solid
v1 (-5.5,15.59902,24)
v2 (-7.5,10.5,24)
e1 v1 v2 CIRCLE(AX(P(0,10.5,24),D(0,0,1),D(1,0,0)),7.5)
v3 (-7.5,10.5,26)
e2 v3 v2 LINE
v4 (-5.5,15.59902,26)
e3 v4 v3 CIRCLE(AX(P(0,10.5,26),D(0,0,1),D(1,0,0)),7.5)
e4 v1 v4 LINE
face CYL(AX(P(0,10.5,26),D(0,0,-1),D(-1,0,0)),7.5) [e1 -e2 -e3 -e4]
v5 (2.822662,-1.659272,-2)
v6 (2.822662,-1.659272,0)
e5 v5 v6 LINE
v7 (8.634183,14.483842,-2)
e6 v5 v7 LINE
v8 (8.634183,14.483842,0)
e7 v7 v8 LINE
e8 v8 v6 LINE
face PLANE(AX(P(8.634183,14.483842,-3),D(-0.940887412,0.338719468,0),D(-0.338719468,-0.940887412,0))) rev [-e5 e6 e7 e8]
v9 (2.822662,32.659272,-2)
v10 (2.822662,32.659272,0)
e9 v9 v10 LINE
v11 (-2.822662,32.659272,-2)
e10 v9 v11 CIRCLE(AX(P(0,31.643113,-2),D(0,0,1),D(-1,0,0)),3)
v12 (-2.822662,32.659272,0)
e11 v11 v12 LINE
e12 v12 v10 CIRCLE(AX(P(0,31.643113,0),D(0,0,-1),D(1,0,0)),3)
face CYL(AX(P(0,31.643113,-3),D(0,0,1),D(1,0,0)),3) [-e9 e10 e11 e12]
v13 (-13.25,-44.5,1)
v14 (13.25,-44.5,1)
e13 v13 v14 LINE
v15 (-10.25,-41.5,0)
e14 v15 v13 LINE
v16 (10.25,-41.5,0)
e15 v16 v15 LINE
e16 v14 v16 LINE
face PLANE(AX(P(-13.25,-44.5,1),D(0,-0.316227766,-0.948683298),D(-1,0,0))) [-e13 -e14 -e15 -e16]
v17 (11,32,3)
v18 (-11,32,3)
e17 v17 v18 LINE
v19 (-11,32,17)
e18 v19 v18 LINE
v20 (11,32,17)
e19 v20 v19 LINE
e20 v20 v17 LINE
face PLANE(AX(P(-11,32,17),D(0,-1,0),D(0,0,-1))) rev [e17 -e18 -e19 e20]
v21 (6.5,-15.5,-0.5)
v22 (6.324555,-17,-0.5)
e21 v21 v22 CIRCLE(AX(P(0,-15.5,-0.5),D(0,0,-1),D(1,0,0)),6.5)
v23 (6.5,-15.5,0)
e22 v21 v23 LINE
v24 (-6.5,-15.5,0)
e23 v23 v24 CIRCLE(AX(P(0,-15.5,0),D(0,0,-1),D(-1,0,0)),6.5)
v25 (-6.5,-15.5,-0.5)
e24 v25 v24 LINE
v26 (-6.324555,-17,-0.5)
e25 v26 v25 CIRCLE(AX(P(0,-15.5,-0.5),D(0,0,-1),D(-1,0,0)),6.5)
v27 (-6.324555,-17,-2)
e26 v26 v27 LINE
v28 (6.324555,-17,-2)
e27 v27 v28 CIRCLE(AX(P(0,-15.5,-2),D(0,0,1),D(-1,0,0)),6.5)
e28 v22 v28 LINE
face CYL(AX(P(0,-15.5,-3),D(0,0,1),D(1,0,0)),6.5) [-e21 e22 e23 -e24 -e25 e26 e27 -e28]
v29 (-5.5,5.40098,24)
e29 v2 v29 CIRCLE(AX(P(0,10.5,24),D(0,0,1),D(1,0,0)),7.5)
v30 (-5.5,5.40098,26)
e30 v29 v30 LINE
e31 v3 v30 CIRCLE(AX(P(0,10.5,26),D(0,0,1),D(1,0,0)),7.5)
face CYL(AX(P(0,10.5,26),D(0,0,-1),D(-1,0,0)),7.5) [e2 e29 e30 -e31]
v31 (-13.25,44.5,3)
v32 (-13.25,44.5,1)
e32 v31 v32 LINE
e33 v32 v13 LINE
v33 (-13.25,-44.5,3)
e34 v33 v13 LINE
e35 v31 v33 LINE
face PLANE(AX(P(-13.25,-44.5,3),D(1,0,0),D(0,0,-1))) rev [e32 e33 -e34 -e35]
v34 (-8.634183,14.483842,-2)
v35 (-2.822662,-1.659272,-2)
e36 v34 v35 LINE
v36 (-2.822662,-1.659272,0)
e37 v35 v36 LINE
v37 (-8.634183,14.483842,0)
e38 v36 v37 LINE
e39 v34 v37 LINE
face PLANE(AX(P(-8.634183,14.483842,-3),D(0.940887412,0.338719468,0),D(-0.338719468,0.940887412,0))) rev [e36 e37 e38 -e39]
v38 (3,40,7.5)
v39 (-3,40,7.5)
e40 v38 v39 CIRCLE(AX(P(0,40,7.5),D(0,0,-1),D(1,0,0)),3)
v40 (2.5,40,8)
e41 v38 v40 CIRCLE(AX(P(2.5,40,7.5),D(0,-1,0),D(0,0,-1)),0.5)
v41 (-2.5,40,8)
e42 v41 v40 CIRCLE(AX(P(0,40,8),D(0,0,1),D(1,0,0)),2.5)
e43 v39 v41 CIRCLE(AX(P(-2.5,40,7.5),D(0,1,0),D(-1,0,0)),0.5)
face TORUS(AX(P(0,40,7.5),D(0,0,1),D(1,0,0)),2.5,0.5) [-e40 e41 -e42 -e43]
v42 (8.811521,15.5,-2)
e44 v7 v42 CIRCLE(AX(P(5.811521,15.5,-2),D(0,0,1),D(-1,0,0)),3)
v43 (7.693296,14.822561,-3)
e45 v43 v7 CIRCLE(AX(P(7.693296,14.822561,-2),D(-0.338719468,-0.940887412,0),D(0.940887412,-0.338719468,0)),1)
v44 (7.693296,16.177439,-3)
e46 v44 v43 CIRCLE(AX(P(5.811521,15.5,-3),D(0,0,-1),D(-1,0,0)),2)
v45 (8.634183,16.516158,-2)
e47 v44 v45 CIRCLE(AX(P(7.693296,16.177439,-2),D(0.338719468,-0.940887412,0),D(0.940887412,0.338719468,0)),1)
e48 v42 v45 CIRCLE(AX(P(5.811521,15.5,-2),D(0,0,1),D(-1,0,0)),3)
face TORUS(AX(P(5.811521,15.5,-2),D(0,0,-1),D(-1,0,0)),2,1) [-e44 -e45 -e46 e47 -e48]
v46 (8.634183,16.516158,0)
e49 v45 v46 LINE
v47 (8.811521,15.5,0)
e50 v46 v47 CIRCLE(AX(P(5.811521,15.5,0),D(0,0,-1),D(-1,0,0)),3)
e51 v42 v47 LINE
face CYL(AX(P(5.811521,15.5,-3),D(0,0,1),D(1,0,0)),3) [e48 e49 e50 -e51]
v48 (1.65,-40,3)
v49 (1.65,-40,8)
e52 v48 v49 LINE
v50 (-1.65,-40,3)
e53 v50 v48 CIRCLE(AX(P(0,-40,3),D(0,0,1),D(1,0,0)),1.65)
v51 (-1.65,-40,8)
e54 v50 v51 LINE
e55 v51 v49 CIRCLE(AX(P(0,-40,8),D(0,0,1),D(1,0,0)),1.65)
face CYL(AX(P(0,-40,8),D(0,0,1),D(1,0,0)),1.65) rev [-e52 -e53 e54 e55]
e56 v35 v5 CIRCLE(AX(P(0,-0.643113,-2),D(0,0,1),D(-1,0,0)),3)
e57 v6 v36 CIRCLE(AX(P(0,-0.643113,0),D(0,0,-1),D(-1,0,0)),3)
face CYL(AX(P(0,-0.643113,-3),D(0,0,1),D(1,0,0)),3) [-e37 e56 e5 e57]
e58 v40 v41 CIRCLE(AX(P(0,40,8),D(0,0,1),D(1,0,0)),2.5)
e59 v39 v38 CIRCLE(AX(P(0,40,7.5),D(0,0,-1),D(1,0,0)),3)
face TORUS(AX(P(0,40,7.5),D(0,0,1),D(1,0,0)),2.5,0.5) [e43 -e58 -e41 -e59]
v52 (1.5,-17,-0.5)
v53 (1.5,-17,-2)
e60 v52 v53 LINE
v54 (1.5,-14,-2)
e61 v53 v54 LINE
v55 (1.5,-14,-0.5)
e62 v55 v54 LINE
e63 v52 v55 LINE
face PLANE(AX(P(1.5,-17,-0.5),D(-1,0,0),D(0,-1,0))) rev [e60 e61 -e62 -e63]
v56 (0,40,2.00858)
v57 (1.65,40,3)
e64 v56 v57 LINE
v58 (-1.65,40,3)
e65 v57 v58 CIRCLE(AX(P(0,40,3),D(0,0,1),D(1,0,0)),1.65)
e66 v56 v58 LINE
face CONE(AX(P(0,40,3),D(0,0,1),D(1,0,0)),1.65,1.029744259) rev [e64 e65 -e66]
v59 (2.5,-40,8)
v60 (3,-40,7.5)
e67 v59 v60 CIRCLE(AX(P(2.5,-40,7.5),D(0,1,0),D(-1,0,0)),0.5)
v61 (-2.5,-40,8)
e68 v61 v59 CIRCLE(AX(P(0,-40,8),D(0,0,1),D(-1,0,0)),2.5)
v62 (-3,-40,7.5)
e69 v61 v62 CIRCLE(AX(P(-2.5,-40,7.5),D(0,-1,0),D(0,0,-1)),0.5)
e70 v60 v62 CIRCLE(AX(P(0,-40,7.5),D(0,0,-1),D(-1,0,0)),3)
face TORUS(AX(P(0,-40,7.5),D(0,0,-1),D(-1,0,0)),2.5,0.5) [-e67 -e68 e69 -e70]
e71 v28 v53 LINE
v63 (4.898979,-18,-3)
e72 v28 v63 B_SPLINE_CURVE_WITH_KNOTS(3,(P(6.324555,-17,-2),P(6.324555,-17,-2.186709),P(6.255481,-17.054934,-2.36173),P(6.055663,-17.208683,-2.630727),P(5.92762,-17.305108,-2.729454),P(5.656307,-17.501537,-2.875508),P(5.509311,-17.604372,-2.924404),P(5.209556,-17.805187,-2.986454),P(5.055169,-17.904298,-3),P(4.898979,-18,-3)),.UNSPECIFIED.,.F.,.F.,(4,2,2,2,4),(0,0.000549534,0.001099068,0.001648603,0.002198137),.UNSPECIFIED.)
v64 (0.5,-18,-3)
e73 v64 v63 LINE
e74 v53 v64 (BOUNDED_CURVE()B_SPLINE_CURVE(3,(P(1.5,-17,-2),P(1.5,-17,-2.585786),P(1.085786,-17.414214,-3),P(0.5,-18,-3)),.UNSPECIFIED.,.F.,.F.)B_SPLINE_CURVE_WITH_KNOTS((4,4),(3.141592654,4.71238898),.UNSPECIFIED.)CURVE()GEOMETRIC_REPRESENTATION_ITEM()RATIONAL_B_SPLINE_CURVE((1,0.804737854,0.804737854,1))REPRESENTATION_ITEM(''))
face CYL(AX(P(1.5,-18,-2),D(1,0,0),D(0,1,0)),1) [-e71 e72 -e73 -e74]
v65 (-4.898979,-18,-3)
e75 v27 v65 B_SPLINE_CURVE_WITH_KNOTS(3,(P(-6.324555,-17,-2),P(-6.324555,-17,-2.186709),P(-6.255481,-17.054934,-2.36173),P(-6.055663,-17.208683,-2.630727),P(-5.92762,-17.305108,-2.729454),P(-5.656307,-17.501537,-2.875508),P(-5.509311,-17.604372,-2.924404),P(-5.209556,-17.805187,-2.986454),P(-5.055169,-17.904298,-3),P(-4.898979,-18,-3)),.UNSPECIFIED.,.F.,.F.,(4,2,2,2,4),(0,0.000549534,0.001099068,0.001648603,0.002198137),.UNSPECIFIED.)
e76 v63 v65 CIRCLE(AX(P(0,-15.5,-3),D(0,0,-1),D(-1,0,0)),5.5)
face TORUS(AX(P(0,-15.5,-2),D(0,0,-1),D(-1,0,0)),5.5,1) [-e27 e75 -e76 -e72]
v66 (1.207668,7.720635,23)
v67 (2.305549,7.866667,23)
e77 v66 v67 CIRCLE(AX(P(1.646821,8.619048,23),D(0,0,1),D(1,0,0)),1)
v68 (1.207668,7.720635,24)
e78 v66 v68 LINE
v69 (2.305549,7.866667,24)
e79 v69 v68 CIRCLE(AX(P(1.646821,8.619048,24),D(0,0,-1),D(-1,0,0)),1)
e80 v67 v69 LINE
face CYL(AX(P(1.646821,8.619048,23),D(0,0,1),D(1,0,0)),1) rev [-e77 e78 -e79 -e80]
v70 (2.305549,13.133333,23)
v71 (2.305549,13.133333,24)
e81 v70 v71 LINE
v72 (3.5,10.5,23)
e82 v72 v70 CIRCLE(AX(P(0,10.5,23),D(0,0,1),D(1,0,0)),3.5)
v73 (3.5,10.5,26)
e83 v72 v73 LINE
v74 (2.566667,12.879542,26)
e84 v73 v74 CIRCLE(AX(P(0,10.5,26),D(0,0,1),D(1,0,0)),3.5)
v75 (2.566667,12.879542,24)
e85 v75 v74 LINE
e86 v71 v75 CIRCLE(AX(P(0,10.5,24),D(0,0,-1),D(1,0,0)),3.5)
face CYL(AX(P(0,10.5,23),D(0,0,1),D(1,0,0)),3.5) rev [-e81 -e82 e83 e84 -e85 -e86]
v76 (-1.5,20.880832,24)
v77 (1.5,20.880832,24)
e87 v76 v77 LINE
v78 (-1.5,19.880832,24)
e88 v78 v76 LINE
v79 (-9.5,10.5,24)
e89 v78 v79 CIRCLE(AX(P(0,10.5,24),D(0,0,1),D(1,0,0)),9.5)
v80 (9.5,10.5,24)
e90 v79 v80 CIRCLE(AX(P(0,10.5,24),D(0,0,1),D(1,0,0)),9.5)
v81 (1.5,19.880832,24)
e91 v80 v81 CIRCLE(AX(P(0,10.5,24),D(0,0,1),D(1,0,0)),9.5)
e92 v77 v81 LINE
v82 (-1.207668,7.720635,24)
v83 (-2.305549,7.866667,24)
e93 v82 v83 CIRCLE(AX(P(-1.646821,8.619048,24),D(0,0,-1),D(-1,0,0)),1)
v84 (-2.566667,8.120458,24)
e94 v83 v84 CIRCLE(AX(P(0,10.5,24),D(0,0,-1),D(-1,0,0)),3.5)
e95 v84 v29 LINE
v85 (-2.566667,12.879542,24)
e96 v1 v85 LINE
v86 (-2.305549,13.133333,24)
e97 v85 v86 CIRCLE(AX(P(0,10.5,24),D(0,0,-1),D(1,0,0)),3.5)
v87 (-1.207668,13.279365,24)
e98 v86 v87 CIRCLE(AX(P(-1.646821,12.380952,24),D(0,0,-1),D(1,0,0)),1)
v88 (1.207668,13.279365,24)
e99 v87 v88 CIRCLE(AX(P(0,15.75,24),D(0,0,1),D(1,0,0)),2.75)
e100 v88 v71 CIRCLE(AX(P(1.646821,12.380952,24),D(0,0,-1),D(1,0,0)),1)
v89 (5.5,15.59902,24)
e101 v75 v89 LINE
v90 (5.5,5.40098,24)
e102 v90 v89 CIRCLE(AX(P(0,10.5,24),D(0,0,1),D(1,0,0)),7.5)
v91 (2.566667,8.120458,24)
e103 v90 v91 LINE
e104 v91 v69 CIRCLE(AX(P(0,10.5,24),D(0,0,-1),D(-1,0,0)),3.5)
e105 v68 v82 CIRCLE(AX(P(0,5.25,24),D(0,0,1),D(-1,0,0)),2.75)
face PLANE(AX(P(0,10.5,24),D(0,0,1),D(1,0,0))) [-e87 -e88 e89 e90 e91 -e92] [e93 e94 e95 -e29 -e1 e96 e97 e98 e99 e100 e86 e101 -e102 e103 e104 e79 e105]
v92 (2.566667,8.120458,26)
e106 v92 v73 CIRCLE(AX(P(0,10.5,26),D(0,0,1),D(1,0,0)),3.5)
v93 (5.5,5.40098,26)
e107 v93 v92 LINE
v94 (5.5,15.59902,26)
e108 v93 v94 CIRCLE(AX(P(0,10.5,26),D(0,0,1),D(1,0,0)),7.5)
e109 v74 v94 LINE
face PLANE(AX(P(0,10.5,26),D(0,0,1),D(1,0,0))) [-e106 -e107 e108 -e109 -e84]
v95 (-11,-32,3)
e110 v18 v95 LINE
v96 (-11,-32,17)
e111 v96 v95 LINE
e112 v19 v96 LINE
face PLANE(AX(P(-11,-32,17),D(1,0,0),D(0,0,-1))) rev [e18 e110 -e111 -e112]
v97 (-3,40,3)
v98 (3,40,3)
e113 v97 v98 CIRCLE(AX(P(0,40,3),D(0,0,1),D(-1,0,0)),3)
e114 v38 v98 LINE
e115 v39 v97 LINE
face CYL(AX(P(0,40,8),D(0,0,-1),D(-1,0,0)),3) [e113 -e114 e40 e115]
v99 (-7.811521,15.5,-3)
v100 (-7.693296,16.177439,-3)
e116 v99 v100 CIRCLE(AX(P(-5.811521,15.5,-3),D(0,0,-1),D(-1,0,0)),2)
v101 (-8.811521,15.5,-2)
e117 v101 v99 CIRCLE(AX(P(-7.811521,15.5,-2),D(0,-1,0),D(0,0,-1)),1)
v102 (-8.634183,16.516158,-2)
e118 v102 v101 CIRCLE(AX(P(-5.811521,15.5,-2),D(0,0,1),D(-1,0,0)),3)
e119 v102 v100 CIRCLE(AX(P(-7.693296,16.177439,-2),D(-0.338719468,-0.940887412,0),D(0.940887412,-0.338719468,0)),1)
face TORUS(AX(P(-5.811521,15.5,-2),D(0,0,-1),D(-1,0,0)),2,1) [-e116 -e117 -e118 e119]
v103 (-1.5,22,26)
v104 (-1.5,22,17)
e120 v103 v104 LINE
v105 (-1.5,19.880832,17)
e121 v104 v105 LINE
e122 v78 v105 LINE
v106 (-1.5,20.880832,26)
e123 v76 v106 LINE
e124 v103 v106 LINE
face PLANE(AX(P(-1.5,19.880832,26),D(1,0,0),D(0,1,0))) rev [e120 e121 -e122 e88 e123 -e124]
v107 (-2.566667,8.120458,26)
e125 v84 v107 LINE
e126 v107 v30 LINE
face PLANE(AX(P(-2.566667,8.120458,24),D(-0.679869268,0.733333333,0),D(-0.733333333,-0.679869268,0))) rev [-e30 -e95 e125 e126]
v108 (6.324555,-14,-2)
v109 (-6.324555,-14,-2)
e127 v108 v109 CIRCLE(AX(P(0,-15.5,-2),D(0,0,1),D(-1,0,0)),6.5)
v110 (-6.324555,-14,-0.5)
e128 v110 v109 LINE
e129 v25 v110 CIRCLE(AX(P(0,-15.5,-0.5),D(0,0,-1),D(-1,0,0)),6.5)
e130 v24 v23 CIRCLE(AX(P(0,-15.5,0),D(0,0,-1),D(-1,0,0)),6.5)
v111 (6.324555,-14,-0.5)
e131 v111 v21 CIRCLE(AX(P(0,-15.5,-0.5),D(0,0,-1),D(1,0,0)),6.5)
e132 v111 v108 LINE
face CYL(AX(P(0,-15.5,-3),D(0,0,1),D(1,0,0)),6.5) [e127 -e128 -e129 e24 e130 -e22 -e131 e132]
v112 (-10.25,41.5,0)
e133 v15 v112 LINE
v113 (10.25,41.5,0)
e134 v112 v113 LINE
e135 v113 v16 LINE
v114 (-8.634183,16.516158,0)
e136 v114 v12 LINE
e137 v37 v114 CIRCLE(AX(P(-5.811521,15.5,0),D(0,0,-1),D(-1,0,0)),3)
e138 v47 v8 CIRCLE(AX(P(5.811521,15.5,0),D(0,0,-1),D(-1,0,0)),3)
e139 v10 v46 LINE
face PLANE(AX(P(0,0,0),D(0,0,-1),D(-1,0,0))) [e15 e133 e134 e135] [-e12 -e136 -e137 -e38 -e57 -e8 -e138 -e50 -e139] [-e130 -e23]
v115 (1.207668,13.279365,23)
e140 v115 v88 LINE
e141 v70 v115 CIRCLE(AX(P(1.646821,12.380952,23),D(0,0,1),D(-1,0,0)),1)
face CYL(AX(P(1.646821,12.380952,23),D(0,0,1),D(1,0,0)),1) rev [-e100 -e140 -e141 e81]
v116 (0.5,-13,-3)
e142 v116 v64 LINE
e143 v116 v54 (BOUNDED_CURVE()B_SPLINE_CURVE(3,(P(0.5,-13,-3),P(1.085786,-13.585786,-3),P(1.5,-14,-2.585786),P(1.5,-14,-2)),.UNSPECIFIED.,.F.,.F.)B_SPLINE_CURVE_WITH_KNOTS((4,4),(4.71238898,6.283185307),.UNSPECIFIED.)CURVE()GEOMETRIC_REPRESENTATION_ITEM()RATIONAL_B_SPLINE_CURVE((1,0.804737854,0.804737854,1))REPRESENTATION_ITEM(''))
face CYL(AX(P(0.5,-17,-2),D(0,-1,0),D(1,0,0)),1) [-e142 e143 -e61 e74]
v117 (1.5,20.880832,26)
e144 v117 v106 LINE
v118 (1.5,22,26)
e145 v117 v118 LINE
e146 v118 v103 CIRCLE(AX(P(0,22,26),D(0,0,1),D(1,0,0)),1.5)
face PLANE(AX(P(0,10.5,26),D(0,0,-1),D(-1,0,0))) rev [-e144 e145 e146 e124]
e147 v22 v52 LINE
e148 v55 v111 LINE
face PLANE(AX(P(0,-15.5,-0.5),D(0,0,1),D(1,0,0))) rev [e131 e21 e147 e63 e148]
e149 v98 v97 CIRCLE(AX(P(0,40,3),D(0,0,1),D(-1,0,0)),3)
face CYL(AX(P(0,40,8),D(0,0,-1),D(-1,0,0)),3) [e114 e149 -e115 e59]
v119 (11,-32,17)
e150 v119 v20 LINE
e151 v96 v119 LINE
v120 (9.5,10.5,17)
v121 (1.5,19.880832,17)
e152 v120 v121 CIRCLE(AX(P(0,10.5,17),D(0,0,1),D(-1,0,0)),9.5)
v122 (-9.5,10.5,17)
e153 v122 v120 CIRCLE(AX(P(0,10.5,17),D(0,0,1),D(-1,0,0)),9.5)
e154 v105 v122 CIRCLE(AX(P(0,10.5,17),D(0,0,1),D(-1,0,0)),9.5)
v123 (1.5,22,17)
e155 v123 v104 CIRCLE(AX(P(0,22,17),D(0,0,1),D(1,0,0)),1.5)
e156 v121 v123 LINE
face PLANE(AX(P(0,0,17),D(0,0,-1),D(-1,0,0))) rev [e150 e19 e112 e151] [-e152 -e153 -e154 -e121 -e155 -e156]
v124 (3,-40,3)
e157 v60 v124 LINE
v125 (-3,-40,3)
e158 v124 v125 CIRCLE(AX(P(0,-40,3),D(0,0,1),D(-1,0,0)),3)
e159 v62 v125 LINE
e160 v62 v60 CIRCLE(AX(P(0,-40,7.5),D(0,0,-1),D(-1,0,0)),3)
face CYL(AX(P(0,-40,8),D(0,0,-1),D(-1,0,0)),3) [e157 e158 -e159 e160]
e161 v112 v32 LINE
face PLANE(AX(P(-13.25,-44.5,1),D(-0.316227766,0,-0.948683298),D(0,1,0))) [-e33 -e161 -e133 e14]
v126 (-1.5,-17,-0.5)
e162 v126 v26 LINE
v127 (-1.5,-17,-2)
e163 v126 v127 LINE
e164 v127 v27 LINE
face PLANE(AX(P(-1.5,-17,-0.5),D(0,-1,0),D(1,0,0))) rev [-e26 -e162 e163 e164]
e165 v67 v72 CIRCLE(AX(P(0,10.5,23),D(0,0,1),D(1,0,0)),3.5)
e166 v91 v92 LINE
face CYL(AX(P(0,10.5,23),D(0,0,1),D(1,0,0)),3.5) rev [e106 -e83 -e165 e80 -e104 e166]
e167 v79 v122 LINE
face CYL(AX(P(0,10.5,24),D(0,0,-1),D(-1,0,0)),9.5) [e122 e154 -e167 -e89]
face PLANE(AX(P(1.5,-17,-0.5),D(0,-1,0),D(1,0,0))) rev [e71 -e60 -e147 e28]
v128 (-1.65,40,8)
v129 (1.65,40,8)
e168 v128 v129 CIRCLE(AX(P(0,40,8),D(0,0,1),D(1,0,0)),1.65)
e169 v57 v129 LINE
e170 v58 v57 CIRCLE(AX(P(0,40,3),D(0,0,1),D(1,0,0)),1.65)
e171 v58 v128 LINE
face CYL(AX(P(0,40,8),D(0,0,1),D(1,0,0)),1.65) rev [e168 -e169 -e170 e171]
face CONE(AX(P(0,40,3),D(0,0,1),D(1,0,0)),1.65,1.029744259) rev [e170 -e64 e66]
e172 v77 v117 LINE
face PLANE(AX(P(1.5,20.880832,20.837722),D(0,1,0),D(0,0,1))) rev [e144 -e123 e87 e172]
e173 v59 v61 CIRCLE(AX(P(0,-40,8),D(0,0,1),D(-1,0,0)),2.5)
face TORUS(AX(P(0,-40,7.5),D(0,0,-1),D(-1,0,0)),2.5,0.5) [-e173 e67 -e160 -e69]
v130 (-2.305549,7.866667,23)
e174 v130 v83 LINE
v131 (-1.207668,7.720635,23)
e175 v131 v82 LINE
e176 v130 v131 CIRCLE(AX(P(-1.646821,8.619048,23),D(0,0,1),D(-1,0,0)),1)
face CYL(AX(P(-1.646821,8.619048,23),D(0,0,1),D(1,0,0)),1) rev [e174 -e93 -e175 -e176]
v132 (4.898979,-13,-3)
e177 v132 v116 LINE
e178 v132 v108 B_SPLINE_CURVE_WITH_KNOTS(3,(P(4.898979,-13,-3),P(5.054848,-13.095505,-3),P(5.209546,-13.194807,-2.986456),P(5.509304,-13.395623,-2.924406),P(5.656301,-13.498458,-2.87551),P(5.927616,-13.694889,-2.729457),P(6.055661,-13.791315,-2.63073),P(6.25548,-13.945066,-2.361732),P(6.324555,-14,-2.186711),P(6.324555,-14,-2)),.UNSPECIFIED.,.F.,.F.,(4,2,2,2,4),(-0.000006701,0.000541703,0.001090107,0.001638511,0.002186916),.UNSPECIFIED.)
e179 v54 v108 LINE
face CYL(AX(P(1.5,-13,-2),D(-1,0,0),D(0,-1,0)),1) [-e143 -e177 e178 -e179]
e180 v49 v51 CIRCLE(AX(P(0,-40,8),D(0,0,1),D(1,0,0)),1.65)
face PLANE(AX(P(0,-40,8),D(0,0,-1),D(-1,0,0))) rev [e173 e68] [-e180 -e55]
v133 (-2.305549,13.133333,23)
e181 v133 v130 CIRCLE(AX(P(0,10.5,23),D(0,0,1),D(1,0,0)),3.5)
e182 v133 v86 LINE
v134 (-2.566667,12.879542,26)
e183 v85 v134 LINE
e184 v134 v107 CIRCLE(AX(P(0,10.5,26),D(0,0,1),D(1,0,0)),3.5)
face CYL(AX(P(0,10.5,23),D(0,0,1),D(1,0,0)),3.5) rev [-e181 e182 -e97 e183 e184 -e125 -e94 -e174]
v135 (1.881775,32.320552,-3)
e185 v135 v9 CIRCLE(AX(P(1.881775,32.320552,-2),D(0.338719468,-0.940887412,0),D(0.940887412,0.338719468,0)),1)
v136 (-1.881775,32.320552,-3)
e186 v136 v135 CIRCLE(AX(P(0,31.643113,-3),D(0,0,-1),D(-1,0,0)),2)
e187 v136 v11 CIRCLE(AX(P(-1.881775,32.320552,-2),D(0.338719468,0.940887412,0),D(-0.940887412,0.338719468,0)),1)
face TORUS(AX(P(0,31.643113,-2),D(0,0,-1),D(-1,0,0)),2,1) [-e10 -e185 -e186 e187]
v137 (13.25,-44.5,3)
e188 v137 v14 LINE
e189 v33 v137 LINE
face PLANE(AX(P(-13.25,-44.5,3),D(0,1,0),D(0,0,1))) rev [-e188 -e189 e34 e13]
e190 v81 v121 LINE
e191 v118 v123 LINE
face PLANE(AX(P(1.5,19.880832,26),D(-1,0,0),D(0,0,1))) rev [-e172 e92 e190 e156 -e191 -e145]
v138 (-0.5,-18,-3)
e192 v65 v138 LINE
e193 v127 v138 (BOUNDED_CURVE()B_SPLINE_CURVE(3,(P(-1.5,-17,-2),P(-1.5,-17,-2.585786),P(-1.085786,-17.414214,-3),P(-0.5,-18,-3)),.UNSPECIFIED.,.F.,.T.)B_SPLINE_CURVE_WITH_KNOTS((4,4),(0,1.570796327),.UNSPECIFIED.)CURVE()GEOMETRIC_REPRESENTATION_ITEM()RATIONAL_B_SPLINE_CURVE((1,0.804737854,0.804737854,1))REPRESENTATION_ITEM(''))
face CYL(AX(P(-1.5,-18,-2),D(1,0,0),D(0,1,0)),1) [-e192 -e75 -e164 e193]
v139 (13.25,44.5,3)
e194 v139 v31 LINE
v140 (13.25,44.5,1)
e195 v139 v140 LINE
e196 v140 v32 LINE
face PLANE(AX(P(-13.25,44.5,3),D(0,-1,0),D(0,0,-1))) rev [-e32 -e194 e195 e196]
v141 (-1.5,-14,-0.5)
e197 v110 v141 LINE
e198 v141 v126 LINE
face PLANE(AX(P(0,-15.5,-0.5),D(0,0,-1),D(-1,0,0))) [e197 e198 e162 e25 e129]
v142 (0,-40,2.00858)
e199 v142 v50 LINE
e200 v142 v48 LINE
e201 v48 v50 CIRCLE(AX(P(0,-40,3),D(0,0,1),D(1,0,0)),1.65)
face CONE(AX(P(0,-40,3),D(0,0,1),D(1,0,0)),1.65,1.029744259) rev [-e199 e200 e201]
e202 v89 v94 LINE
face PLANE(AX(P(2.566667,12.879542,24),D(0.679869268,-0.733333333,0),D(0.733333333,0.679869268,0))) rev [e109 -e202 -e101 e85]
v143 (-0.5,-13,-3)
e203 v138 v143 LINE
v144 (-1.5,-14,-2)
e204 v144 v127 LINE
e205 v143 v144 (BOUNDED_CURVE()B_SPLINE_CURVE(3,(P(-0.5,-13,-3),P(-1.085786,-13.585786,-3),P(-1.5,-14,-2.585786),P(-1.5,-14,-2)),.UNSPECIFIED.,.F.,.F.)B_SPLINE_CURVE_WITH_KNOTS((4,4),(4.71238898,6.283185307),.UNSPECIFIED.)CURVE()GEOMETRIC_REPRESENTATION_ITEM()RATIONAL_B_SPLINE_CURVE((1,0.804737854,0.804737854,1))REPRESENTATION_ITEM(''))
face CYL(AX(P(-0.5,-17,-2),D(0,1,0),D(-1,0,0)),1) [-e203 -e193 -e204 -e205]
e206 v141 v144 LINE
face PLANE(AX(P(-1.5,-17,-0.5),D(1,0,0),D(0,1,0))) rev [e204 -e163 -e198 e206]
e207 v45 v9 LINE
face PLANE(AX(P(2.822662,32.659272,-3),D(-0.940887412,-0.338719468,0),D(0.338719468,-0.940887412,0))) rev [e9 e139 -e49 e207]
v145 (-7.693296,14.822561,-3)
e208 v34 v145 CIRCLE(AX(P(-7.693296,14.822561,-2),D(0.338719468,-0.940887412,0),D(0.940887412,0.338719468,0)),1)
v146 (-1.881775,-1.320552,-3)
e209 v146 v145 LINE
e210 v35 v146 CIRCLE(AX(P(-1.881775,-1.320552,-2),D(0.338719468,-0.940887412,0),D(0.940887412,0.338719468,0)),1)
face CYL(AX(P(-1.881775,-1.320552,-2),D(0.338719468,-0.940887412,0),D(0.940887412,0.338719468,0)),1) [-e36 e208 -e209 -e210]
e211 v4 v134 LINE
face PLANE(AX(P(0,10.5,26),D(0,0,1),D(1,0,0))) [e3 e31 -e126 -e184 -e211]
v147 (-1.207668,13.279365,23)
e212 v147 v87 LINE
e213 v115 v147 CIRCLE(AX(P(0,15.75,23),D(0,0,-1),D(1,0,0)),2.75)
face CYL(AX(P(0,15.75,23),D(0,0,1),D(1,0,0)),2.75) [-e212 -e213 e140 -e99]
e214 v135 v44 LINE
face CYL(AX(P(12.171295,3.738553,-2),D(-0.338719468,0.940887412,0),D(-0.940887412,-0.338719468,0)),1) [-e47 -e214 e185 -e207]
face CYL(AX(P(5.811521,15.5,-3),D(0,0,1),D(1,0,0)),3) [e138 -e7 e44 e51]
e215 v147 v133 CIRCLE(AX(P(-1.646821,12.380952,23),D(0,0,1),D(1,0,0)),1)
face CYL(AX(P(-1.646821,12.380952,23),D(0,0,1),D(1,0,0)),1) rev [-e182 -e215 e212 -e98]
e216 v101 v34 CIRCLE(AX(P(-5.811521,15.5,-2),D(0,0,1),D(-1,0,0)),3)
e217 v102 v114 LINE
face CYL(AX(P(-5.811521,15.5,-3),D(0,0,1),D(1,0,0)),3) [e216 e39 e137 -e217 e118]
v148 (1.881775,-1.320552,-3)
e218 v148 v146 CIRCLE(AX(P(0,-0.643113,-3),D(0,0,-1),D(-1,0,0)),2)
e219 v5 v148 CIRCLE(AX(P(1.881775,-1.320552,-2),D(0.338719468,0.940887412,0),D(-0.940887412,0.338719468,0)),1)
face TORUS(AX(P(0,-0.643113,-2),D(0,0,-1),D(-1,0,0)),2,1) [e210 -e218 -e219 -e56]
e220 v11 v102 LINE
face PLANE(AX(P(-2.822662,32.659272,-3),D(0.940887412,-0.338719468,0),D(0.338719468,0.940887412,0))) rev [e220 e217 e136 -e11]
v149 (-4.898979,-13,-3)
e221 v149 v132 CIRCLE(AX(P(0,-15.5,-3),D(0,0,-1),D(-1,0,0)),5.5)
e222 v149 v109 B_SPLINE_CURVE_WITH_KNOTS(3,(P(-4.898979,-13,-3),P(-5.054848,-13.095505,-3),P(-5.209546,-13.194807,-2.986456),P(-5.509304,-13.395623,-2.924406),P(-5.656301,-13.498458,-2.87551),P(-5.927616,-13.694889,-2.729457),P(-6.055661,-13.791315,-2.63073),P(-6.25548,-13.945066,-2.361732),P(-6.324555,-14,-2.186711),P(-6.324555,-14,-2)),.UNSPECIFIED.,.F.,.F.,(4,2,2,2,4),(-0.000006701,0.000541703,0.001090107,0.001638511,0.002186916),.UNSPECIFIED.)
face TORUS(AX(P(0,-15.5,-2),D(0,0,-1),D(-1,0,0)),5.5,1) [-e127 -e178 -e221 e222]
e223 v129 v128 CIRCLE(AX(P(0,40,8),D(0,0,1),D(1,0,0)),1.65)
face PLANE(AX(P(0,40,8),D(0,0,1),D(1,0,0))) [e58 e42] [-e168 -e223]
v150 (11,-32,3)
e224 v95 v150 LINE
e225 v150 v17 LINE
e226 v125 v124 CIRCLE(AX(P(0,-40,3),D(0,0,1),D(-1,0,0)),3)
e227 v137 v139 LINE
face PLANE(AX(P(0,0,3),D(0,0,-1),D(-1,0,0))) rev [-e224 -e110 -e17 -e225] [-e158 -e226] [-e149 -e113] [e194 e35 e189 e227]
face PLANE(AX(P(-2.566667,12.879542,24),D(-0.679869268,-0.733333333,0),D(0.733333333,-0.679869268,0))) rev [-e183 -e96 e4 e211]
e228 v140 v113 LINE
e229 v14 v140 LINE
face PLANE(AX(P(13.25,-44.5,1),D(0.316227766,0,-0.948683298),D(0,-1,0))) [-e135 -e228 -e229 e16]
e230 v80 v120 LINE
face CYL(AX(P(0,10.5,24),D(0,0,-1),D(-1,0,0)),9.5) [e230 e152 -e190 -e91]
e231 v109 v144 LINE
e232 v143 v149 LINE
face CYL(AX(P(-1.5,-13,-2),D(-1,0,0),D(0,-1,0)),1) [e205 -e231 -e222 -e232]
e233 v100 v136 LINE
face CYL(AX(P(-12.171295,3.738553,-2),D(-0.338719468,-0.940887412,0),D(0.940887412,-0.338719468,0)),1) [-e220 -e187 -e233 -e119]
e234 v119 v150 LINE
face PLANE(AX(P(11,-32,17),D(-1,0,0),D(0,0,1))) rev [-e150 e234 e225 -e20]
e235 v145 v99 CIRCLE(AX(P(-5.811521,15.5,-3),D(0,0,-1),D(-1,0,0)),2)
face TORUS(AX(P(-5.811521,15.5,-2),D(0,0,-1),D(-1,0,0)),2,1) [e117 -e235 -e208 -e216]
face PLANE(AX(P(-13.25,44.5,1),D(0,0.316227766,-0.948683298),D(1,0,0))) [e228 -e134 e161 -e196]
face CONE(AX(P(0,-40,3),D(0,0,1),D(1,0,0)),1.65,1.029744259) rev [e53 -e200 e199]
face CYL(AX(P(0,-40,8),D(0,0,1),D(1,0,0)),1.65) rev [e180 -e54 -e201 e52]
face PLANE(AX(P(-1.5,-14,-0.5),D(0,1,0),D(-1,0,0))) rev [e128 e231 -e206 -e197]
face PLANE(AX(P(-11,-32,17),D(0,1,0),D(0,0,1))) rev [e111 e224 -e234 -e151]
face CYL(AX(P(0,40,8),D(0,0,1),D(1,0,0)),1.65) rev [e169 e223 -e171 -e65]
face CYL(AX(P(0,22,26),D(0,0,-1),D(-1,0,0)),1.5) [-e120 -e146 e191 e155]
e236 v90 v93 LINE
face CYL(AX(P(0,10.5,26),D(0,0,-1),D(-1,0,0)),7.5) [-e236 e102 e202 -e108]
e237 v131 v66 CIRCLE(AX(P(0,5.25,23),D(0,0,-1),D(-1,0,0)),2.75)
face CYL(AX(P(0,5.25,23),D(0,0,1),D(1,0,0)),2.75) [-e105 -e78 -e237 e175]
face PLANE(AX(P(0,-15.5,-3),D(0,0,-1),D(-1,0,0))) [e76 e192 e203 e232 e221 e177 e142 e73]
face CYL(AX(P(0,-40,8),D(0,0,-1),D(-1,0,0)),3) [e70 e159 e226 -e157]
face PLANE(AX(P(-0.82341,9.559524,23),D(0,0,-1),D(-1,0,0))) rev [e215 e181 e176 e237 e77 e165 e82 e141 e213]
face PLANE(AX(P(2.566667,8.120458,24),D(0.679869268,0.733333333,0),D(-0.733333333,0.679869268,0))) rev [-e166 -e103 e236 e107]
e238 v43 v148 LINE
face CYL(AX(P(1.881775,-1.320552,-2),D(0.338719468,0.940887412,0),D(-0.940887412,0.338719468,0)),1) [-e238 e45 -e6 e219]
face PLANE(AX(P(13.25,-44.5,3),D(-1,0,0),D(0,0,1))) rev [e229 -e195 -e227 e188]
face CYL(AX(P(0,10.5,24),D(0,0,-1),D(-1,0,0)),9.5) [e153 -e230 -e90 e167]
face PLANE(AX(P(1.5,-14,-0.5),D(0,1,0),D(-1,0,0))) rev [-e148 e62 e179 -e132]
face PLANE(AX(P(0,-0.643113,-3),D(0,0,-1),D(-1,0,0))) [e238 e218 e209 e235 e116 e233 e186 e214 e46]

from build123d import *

# Parameters (mm, degrees)
SKETCH1_W             = 26.5
SKETCH1_H             = 89
BOSS_EXTRUDE1_DEPTH   = 3
SKETCH2_W             = 22
SKETCH2_H             = 64
BOSS_EXTRUDE2_DEPTH   = 14
SKETCH3_R             = 3
BOSS_EXTRUDE3_DEPTH   = 5
M4_TAPPED_HOLE1_D     = 3.3
M4_TAPPED_HOLE1_DEPTH = 5
M4_TAPPED_HOLE1_TIP   = 0.991420021
CHAMFER1_SIZE         = 3
CHAMFER1_SIZE2        = 1
SKETCH6_R             = 9.5
BOSS_EXTRUDE4_DEPTH   = 7
BOSS_EXTRUDE5_DEPTH   = 9
CUT_EXTRUDE1_START    = -2
CUT_EXTRUDE1_DEPTH    = 2
SKETCH9_R             = 7.5
BOSS_EXTRUDE6_DEPTH   = 2
CUT_EXTRUDE5_DEPTH    = 3
CUT_EXTRUDE6_DEPTH    = 2
SKETCH14_R            = 6.5
BOSS_EXTRUDE7_DEPTH   = 3
CUT_EXTRUDE7_START    = -2.5
CUT_EXTRUDE7_DEPTH    = 2.5
FILLET1_R             = 1
BOSS_EXTRUDE8_DEPTH   = 3
FILLET2_R             = 1
FILLET3_R             = 0.5


with BuildPart() as part:
    # Sketch1 → Boss-Extrude1 (new body)
    with BuildSketch(Plane.XY):
        Rectangle(SKETCH1_W, SKETCH1_H)
    extrude(amount=BOSS_EXTRUDE1_DEPTH)

    # Sketch2 → Boss-Extrude2 (add)
    with BuildSketch(Plane.XY.offset(3)):
        Rectangle(SKETCH2_W, SKETCH2_H)
    extrude(amount=BOSS_EXTRUDE2_DEPTH)

    # Sketch3 → Boss-Extrude3 (add)
    with BuildSketch(Plane.XY.offset(3)):
        with Locations(Location((0, 40, 0), (0, 0, 180))):
            Circle(SKETCH3_R)
        with Locations(Location((0, -40, 0), (0, 0, 180))):
            Circle(SKETCH3_R)
    extrude(amount=BOSS_EXTRUDE3_DEPTH)

    # M4 Tapped Hole1
    with Locations(Plane.XY.offset(8)):
        with Locations((0, 40), (0, -40)):
            Hole(M4_TAPPED_HOLE1_D / 2, depth=M4_TAPPED_HOLE1_DEPTH)
            with Locations((0, 0, -(M4_TAPPED_HOLE1_DEPTH + M4_TAPPED_HOLE1_TIP / 2))):  # 118° drill point
                Cone(0, M4_TAPPED_HOLE1_D / 2, M4_TAPPED_HOLE1_TIP, mode=Mode.SUBTRACT)

    # Chamfer1
    chamfer1_edges = [part.edges().sort_by_distance(p)[0] for p in [
        (0, -44.5, 0),
        (-13.25, 0, 0),
        (0, 44.5, 0),
        (13.25, 0, 0),
    ]]
    chamfer1_side = [part.faces().sort_by_distance(p)[0] for p in [
        (0, 0, 0),
    ]]
    chamfer(chamfer1_edges, length=CHAMFER1_SIZE, length2=CHAMFER1_SIZE2, reference=chamfer1_side[0])

    # Sketch6 → Boss-Extrude4 (add)
    with BuildSketch(Plane.XY.offset(17)):
        with Locations(Location((0, 10.5, 0), (0, 0, 180))):
            Circle(SKETCH6_R)
    extrude(amount=BOSS_EXTRUDE4_DEPTH)

    # Sketch7 → Boss-Extrude5 (add)
    with BuildSketch(Plane.XY.offset(17)):
        with BuildLine():
            Line((-1.5, 19.88083152), (-1.5, 22))
            ThreePointArc((-1.5, 22), (0, 23.5), (1.5, 22))
            Line((1.5, 22), (1.5, 19.88083152))
            ThreePointArc((1.5, 19.88083152), (0, 20), (-1.5, 19.88083152))
        make_face()
    extrude(amount=BOSS_EXTRUDE5_DEPTH)

    # Sketch8 → Cut-Extrude1 (cut)
    with BuildSketch(Plane.XY.offset(26).offset(CUT_EXTRUDE1_START)):
        with BuildLine():
            Line((1.5, 20.88083152), (-1.5, 20.88083152))
            Line((-1.5, 20.88083152), (-1.5, 19.88083152))
            ThreePointArc((-1.5, 19.88083152), (0, 20), (1.5, 19.88083152))
            Line((1.5, 19.88083152), (1.5, 20.88083152))
        make_face()
    extrude(amount=CUT_EXTRUDE1_DEPTH, mode=Mode.SUBTRACT)

    # Sketch9 → Boss-Extrude6 (add)
    with BuildSketch(Plane.XY.offset(24)):
        with Locations((0, 10.5)):
            Circle(SKETCH9_R)
    extrude(amount=BOSS_EXTRUDE6_DEPTH)

    # Sketch12 → Cut-Extrude5 (cut)
    with BuildSketch(Plane.XY.offset(26)):
        with BuildLine():
            ThreePointArc((-2.305548862, 13.133333333), (-3.5, 10.5), (-2.305548862, 7.866666667))
            ThreePointArc((-2.305548862, 7.866666667), (-1.778671788, 7.627778095), (-1.207668452, 7.720634921))
            ThreePointArc((-1.207668452, 7.720634921), (0, 8), (1.207668452, 7.720634921))
            ThreePointArc((1.207668452, 7.720634921), (1.778671788, 7.627778095), (2.305548862, 7.866666667))
            ThreePointArc((2.305548862, 7.866666667), (3.5, 10.5), (2.305548862, 13.133333333))
            ThreePointArc((2.305548862, 13.133333333), (1.778671788, 13.372221905), (1.207668452, 13.279365079))
            ThreePointArc((1.207668452, 13.279365079), (0, 13), (-1.207668452, 13.279365079))
            ThreePointArc((-1.207668452, 13.279365079), (-1.778671788, 13.372221905), (-2.305548862, 13.133333333))
        make_face()
    extrude(amount=-CUT_EXTRUDE5_DEPTH, mode=Mode.SUBTRACT)

    # Sketch13 → Cut-Extrude6 (cut)
    with BuildSketch(Plane.XY.offset(26)):
        with BuildLine():
            Line((2.566666667, 12.87954244), (5.5, 15.599019514))
            ThreePointArc((5.5, 15.599019514), (0, 18), (-5.5, 15.599019514))
            Line((-5.5, 15.599019514), (-2.566666667, 12.87954244))
            ThreePointArc((-2.566666667, 12.87954244), (-2.439410481, 13.009835952), (-2.305548862, 13.133333333))
            ThreePointArc((-2.305548862, 13.133333333), (-1.778671788, 13.372221905), (-1.207668452, 13.279365079))
            ThreePointArc((-1.207668452, 13.279365079), (0, 13), (1.207668452, 13.279365079))
            ThreePointArc((1.207668452, 13.279365079), (1.778671788, 13.372221905), (2.305548862, 13.133333333))
            ThreePointArc((2.305548862, 13.133333333), (2.439410481, 13.009835952), (2.566666667, 12.87954244))
        make_face()
        with BuildLine():
            Line((-2.566666667, 8.12045756), (-5.5, 5.400980486))
            ThreePointArc((-5.5, 5.400980486), (0, 3), (5.5, 5.400980486))
            Line((5.5, 5.400980486), (2.566666667, 8.12045756))
            ThreePointArc((2.566666667, 8.12045756), (2.439410481, 7.990164048), (2.305548862, 7.866666667))
            ThreePointArc((2.305548862, 7.866666667), (1.778671788, 7.627778095), (1.207668452, 7.720634921))
            ThreePointArc((1.207668452, 7.720634921), (0, 8), (-1.207668452, 7.720634921))
            ThreePointArc((-1.207668452, 7.720634921), (-1.778671788, 7.627778095), (-2.305548862, 7.866666667))
            ThreePointArc((-2.305548862, 7.866666667), (-2.439410481, 7.990164048), (-2.566666667, 8.12045756))
        make_face()
    extrude(amount=-CUT_EXTRUDE6_DEPTH, mode=Mode.SUBTRACT)

    # Sketch14 → Boss-Extrude7 (add)
    with BuildSketch(Plane(origin=(0, 0, 0), x_dir=(-1, 0, 0), z_dir=(0, 0, -1))):
        with Locations((0, -15.5)):
            Circle(SKETCH14_R)
    extrude(amount=BOSS_EXTRUDE7_DEPTH)

    # Sketch15 → Cut-Extrude7 (cut)
    with BuildSketch(Plane(origin=(0, 0, -3), x_dir=(-1, 0, 0), z_dir=(0, 0, -1)).offset(CUT_EXTRUDE7_START)):
        with BuildLine():
            Line((1.5, -17), (6.32455532, -17))
            ThreePointArc((6.32455532, -17), (6.5, -15.5), (6.32455532, -14))
            Line((6.32455532, -14), (1.5, -14))
            Line((1.5, -14), (1.5, -17))
        make_face()
        with BuildLine():
            Line((-1.5, -14), (-6.32455532, -14))
            ThreePointArc((-6.32455532, -14), (-6.5, -15.5), (-6.32455532, -17))
            Line((-6.32455532, -17), (-1.5, -17))
            Line((-1.5, -17), (-1.5, -14))
        make_face()
    extrude(amount=CUT_EXTRUDE7_DEPTH, mode=Mode.SUBTRACT)

    # Fillet1
    fillet1_edges = [part.edges().sort_by_distance(p)[0] for p in [
        (0, -9, -3),
        (-3.91227766, -14, -3),
        (-1.5, -15.5, -3),
        (-3.91227766, -17, -3),
        (0, -22, -3),
        (1.5, -15.5, -3),
        (3.91227766, -14, -3),
        (3.91227766, -17, -3),
    ]]
    fillet(fillet1_edges, radius=FILLET1_R)

    # Sketch16 → Boss-Extrude8 (add)
    with BuildSketch(Plane(origin=(0, 0, 0), x_dir=(-1, 0, 0), z_dir=(0, 0, -1))):
        with BuildLine():
            Line((-2.822662236, 32.659271568), (-8.634182974, 16.516158405))
            ThreePointArc((-8.634182974, 16.516158405), (-8.811520739, 15.5), (-8.634182974, 14.483841595))
            Line((-8.634182974, 14.483841595), (-2.822662236, -1.659271568))
            ThreePointArc((-2.822662236, -1.659271568), (0, -3.643113163), (2.822662236, -1.659271568))
            Line((2.822662236, -1.659271568), (8.634182974, 14.483841595))
            ThreePointArc((8.634182974, 14.483841595), (8.811520739, 15.5), (8.634182974, 16.516158405))
            Line((8.634182974, 16.516158405), (2.822662236, 32.659271568))
            ThreePointArc((2.822662236, 32.659271568), (0, 34.643113163), (-2.822662236, 32.659271568))
        make_face()
    extrude(amount=BOSS_EXTRUDE8_DEPTH)

    # Fillet2
    fillet2_edges = [part.edges().sort_by_distance(p)[0] for p in [
        (0, -3.643113163, -3),
        (-5.728422605, 6.412285014, -3),
        (-8.811520739, 15.5, -3),
        (-5.728422605, 24.587714986, -3),
        (0, 34.643113163, -3),
        (5.728422605, 24.587714986, -3),
        (8.811520739, 15.5, -3),
        (5.728422605, 6.412285014, -3),
    ]]
    fillet(fillet2_edges, radius=FILLET2_R)

    # Fillet3
    fillet3_edges = [part.edges().sort_by_distance(p)[0] for p in [
        (3, 40, 8),
        (3, -40, 8),
    ]]
    fillet(fillet3_edges, radius=FILLET3_R)


solid = part.part
